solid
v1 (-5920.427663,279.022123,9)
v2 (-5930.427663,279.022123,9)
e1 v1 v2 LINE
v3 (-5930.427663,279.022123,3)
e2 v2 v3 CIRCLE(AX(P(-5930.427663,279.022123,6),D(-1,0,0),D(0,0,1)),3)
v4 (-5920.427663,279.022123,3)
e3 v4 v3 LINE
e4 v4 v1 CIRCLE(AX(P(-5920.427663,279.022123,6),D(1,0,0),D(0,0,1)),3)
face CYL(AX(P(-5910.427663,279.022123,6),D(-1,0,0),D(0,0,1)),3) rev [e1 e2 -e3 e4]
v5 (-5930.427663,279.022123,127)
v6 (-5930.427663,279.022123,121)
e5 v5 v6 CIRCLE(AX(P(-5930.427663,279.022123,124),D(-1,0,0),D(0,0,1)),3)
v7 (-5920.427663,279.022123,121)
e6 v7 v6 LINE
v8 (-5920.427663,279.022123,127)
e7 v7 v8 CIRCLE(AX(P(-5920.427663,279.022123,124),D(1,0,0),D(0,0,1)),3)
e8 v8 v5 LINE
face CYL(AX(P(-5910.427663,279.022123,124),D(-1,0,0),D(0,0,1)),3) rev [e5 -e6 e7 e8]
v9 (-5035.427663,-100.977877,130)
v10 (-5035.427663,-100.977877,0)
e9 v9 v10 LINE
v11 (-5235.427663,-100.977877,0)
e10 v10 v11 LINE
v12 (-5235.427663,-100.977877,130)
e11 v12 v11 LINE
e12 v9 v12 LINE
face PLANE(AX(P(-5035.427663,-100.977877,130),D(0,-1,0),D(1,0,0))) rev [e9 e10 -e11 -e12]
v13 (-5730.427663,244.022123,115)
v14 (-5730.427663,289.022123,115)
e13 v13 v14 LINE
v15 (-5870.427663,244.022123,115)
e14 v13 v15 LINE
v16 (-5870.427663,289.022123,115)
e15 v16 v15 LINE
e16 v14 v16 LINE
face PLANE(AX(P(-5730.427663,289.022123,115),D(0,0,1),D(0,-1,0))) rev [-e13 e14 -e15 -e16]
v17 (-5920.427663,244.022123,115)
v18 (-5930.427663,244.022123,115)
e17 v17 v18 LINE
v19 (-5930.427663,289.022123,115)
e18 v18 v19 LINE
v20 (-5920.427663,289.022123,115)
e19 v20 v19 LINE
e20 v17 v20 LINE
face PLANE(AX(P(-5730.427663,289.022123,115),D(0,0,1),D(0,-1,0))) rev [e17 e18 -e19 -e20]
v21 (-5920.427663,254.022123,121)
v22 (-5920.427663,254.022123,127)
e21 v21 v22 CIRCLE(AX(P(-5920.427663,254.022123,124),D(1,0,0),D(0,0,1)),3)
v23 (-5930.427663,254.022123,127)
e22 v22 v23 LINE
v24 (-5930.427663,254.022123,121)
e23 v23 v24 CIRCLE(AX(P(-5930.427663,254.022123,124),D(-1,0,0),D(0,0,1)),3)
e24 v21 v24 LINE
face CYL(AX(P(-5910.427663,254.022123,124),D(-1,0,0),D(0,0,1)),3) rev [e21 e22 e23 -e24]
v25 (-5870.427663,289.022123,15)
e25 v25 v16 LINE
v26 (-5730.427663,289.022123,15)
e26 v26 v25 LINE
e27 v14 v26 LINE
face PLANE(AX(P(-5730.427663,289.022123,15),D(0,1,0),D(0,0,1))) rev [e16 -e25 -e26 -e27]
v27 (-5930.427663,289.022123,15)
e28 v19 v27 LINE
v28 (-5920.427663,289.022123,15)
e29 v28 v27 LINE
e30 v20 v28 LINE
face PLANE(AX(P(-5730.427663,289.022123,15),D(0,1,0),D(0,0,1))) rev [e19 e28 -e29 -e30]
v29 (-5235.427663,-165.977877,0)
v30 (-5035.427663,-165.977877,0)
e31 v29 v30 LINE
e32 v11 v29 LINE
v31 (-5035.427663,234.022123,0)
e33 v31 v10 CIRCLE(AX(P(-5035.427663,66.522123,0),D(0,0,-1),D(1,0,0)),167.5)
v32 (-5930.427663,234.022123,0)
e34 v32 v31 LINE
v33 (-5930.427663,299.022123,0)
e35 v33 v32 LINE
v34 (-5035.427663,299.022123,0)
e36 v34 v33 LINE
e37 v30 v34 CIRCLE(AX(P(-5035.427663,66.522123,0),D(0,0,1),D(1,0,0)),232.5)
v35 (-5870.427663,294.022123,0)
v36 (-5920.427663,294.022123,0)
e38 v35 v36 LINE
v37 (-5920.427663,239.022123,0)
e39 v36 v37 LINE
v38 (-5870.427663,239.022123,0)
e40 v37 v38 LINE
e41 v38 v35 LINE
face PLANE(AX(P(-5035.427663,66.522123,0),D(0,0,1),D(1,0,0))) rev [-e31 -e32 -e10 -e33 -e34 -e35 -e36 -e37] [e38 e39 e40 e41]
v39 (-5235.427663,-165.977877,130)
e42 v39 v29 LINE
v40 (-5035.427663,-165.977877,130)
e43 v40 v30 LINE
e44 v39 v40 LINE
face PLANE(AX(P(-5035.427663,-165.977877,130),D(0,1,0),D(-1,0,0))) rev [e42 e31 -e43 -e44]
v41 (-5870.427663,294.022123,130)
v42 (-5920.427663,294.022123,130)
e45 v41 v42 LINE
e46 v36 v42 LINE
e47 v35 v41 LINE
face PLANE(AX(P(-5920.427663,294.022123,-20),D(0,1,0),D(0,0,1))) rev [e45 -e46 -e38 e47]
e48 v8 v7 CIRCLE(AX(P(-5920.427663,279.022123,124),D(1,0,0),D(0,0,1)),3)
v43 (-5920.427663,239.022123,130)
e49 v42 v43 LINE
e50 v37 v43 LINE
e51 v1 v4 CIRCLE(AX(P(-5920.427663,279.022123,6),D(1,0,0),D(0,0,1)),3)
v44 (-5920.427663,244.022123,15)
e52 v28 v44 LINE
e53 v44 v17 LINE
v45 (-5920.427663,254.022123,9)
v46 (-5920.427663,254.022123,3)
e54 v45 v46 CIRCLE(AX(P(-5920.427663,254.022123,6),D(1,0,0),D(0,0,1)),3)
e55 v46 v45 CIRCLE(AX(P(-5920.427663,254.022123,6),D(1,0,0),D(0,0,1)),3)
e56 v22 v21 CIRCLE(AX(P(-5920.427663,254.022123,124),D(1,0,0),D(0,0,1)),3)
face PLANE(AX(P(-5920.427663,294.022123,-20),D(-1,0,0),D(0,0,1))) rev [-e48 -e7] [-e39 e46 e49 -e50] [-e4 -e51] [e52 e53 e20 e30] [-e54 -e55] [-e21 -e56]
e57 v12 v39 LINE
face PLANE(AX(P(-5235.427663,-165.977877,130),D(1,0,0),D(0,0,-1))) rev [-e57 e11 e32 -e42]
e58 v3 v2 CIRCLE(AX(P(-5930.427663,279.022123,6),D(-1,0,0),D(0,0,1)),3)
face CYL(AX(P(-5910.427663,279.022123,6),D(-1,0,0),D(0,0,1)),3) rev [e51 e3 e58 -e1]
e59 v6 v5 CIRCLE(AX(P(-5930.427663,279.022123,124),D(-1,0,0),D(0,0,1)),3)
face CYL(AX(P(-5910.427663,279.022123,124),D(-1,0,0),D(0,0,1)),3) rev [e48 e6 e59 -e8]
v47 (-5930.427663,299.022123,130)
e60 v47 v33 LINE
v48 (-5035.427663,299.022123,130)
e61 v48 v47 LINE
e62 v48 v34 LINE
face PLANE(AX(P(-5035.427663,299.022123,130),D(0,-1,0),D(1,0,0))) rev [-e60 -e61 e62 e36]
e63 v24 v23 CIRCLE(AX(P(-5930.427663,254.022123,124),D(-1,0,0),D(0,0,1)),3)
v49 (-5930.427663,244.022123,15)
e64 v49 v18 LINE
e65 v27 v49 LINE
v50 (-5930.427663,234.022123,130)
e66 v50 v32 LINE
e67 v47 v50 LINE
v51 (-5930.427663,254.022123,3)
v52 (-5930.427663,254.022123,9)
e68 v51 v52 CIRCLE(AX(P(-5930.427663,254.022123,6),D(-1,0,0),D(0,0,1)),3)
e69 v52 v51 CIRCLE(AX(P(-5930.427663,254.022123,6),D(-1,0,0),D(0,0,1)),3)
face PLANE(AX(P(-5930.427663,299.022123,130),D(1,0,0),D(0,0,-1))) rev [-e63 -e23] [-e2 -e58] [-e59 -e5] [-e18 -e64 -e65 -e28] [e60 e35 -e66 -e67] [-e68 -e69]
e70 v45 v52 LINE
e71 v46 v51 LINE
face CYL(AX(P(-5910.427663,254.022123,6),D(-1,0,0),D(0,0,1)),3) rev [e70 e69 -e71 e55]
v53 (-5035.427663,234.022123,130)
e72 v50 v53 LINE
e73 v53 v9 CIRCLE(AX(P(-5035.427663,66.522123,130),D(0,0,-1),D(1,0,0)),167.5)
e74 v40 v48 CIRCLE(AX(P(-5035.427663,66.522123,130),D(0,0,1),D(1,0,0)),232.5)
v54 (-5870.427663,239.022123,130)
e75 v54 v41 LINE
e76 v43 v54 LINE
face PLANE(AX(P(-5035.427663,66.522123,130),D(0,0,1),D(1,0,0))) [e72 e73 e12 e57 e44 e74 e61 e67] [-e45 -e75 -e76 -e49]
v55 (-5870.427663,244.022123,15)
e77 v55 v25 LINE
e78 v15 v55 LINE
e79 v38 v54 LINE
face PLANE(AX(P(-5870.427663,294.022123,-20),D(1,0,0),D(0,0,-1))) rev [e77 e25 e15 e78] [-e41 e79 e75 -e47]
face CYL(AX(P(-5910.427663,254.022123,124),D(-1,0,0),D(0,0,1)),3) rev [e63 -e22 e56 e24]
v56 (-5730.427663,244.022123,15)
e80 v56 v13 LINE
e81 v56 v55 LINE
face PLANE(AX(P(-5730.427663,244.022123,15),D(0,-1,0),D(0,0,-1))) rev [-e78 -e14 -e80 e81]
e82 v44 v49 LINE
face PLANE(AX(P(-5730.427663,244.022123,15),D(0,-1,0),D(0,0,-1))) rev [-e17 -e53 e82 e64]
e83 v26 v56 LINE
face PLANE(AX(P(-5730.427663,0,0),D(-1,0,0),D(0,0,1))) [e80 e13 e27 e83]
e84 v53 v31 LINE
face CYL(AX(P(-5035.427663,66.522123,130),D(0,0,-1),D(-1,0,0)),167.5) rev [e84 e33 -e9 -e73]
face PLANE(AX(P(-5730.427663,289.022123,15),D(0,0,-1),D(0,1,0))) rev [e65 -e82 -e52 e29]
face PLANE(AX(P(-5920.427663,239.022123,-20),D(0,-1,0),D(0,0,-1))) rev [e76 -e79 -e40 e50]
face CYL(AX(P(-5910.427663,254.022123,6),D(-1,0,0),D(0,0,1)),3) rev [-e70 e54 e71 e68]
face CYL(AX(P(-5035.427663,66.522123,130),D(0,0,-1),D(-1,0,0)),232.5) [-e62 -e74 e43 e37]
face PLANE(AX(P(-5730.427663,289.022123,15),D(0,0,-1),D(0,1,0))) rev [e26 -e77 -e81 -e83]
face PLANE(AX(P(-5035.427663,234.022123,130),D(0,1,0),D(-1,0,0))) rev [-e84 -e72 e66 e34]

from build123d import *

# Parameters (mm, degrees)
EXTRUDE_1_DEPTH     = 130
SKETCH_2_R          = 3
CUT_EXTRUDE_1_DEPTH = 20
SKETCH_9_W          = 50
SKETCH_9_H          = 55
CUT_EXTRUDE_2_DEPTH = 150
SKETCH_10_W         = 100
SKETCH_10_H         = 45
CUT_EXTRUDE_3_DEPTH = 200


with BuildPart() as part:
    # 草图1 → 凸台-拉伸1 (new body)
    with BuildSketch(Plane.XY):
        with BuildLine():
            Line((-5035.427662897, 234.022122697), (-5930.427662897, 234.022122697))
            Line((-5930.427662897, 234.022122697), (-5930.427662897, 299.022122697))
            Line((-5930.427662897, 299.022122697), (-5035.427662897, 299.022122697))
            ThreePointArc((-5035.427662897, 299.022122697), (-4802.927662897, 66.522122697), (-5035.427662897, -165.977877303))
            Line((-5035.427662897, -165.977877303), (-5235.427662897, -165.977877303))
            Line((-5235.427662897, -165.977877303), (-5235.427662897, -100.977877303))
            Line((-5235.427662897, -100.977877303), (-5035.427662897, -100.977877303))
            ThreePointArc((-5035.427662897, -100.977877303), (-4867.927662897, 66.522122697), (-5035.427662897, 234.022122697))
        make_face()
    extrude(amount=EXTRUDE_1_DEPTH)

    # 草图2 → 切除-拉伸1 (cut)
    with BuildSketch(Plane.ZY.offset(5930.427662897)):
        with Locations((6, 279.022122697)):
            Circle(SKETCH_2_R)
        with Locations((6, 254.022122697)):
            Circle(SKETCH_2_R)
        with Locations((124, 279.022122697)):
            Circle(SKETCH_2_R)
        with Locations((124, 254.022122697)):
            Circle(SKETCH_2_R)
    extrude(amount=-CUT_EXTRUDE_1_DEPTH, mode=Mode.SUBTRACT)

    # 草图9 → 切除-拉伸2 (cut)
    with BuildSketch(Plane.XY.offset(130)):
        with Locations((-5895.427662897, 266.522122697)):
            Rectangle(SKETCH_9_W, SKETCH_9_H)
    extrude(amount=-CUT_EXTRUDE_2_DEPTH, mode=Mode.SUBTRACT)

    # 草图10 → 切除-拉伸3 (cut)
    with BuildSketch(Plane.ZY.offset(5930.427662897)):
        with Locations((65, 266.522122697)):
            Rectangle(SKETCH_10_W, SKETCH_10_H)
    extrude(amount=-CUT_EXTRUDE_3_DEPTH, mode=Mode.SUBTRACT)


solid = part.part
